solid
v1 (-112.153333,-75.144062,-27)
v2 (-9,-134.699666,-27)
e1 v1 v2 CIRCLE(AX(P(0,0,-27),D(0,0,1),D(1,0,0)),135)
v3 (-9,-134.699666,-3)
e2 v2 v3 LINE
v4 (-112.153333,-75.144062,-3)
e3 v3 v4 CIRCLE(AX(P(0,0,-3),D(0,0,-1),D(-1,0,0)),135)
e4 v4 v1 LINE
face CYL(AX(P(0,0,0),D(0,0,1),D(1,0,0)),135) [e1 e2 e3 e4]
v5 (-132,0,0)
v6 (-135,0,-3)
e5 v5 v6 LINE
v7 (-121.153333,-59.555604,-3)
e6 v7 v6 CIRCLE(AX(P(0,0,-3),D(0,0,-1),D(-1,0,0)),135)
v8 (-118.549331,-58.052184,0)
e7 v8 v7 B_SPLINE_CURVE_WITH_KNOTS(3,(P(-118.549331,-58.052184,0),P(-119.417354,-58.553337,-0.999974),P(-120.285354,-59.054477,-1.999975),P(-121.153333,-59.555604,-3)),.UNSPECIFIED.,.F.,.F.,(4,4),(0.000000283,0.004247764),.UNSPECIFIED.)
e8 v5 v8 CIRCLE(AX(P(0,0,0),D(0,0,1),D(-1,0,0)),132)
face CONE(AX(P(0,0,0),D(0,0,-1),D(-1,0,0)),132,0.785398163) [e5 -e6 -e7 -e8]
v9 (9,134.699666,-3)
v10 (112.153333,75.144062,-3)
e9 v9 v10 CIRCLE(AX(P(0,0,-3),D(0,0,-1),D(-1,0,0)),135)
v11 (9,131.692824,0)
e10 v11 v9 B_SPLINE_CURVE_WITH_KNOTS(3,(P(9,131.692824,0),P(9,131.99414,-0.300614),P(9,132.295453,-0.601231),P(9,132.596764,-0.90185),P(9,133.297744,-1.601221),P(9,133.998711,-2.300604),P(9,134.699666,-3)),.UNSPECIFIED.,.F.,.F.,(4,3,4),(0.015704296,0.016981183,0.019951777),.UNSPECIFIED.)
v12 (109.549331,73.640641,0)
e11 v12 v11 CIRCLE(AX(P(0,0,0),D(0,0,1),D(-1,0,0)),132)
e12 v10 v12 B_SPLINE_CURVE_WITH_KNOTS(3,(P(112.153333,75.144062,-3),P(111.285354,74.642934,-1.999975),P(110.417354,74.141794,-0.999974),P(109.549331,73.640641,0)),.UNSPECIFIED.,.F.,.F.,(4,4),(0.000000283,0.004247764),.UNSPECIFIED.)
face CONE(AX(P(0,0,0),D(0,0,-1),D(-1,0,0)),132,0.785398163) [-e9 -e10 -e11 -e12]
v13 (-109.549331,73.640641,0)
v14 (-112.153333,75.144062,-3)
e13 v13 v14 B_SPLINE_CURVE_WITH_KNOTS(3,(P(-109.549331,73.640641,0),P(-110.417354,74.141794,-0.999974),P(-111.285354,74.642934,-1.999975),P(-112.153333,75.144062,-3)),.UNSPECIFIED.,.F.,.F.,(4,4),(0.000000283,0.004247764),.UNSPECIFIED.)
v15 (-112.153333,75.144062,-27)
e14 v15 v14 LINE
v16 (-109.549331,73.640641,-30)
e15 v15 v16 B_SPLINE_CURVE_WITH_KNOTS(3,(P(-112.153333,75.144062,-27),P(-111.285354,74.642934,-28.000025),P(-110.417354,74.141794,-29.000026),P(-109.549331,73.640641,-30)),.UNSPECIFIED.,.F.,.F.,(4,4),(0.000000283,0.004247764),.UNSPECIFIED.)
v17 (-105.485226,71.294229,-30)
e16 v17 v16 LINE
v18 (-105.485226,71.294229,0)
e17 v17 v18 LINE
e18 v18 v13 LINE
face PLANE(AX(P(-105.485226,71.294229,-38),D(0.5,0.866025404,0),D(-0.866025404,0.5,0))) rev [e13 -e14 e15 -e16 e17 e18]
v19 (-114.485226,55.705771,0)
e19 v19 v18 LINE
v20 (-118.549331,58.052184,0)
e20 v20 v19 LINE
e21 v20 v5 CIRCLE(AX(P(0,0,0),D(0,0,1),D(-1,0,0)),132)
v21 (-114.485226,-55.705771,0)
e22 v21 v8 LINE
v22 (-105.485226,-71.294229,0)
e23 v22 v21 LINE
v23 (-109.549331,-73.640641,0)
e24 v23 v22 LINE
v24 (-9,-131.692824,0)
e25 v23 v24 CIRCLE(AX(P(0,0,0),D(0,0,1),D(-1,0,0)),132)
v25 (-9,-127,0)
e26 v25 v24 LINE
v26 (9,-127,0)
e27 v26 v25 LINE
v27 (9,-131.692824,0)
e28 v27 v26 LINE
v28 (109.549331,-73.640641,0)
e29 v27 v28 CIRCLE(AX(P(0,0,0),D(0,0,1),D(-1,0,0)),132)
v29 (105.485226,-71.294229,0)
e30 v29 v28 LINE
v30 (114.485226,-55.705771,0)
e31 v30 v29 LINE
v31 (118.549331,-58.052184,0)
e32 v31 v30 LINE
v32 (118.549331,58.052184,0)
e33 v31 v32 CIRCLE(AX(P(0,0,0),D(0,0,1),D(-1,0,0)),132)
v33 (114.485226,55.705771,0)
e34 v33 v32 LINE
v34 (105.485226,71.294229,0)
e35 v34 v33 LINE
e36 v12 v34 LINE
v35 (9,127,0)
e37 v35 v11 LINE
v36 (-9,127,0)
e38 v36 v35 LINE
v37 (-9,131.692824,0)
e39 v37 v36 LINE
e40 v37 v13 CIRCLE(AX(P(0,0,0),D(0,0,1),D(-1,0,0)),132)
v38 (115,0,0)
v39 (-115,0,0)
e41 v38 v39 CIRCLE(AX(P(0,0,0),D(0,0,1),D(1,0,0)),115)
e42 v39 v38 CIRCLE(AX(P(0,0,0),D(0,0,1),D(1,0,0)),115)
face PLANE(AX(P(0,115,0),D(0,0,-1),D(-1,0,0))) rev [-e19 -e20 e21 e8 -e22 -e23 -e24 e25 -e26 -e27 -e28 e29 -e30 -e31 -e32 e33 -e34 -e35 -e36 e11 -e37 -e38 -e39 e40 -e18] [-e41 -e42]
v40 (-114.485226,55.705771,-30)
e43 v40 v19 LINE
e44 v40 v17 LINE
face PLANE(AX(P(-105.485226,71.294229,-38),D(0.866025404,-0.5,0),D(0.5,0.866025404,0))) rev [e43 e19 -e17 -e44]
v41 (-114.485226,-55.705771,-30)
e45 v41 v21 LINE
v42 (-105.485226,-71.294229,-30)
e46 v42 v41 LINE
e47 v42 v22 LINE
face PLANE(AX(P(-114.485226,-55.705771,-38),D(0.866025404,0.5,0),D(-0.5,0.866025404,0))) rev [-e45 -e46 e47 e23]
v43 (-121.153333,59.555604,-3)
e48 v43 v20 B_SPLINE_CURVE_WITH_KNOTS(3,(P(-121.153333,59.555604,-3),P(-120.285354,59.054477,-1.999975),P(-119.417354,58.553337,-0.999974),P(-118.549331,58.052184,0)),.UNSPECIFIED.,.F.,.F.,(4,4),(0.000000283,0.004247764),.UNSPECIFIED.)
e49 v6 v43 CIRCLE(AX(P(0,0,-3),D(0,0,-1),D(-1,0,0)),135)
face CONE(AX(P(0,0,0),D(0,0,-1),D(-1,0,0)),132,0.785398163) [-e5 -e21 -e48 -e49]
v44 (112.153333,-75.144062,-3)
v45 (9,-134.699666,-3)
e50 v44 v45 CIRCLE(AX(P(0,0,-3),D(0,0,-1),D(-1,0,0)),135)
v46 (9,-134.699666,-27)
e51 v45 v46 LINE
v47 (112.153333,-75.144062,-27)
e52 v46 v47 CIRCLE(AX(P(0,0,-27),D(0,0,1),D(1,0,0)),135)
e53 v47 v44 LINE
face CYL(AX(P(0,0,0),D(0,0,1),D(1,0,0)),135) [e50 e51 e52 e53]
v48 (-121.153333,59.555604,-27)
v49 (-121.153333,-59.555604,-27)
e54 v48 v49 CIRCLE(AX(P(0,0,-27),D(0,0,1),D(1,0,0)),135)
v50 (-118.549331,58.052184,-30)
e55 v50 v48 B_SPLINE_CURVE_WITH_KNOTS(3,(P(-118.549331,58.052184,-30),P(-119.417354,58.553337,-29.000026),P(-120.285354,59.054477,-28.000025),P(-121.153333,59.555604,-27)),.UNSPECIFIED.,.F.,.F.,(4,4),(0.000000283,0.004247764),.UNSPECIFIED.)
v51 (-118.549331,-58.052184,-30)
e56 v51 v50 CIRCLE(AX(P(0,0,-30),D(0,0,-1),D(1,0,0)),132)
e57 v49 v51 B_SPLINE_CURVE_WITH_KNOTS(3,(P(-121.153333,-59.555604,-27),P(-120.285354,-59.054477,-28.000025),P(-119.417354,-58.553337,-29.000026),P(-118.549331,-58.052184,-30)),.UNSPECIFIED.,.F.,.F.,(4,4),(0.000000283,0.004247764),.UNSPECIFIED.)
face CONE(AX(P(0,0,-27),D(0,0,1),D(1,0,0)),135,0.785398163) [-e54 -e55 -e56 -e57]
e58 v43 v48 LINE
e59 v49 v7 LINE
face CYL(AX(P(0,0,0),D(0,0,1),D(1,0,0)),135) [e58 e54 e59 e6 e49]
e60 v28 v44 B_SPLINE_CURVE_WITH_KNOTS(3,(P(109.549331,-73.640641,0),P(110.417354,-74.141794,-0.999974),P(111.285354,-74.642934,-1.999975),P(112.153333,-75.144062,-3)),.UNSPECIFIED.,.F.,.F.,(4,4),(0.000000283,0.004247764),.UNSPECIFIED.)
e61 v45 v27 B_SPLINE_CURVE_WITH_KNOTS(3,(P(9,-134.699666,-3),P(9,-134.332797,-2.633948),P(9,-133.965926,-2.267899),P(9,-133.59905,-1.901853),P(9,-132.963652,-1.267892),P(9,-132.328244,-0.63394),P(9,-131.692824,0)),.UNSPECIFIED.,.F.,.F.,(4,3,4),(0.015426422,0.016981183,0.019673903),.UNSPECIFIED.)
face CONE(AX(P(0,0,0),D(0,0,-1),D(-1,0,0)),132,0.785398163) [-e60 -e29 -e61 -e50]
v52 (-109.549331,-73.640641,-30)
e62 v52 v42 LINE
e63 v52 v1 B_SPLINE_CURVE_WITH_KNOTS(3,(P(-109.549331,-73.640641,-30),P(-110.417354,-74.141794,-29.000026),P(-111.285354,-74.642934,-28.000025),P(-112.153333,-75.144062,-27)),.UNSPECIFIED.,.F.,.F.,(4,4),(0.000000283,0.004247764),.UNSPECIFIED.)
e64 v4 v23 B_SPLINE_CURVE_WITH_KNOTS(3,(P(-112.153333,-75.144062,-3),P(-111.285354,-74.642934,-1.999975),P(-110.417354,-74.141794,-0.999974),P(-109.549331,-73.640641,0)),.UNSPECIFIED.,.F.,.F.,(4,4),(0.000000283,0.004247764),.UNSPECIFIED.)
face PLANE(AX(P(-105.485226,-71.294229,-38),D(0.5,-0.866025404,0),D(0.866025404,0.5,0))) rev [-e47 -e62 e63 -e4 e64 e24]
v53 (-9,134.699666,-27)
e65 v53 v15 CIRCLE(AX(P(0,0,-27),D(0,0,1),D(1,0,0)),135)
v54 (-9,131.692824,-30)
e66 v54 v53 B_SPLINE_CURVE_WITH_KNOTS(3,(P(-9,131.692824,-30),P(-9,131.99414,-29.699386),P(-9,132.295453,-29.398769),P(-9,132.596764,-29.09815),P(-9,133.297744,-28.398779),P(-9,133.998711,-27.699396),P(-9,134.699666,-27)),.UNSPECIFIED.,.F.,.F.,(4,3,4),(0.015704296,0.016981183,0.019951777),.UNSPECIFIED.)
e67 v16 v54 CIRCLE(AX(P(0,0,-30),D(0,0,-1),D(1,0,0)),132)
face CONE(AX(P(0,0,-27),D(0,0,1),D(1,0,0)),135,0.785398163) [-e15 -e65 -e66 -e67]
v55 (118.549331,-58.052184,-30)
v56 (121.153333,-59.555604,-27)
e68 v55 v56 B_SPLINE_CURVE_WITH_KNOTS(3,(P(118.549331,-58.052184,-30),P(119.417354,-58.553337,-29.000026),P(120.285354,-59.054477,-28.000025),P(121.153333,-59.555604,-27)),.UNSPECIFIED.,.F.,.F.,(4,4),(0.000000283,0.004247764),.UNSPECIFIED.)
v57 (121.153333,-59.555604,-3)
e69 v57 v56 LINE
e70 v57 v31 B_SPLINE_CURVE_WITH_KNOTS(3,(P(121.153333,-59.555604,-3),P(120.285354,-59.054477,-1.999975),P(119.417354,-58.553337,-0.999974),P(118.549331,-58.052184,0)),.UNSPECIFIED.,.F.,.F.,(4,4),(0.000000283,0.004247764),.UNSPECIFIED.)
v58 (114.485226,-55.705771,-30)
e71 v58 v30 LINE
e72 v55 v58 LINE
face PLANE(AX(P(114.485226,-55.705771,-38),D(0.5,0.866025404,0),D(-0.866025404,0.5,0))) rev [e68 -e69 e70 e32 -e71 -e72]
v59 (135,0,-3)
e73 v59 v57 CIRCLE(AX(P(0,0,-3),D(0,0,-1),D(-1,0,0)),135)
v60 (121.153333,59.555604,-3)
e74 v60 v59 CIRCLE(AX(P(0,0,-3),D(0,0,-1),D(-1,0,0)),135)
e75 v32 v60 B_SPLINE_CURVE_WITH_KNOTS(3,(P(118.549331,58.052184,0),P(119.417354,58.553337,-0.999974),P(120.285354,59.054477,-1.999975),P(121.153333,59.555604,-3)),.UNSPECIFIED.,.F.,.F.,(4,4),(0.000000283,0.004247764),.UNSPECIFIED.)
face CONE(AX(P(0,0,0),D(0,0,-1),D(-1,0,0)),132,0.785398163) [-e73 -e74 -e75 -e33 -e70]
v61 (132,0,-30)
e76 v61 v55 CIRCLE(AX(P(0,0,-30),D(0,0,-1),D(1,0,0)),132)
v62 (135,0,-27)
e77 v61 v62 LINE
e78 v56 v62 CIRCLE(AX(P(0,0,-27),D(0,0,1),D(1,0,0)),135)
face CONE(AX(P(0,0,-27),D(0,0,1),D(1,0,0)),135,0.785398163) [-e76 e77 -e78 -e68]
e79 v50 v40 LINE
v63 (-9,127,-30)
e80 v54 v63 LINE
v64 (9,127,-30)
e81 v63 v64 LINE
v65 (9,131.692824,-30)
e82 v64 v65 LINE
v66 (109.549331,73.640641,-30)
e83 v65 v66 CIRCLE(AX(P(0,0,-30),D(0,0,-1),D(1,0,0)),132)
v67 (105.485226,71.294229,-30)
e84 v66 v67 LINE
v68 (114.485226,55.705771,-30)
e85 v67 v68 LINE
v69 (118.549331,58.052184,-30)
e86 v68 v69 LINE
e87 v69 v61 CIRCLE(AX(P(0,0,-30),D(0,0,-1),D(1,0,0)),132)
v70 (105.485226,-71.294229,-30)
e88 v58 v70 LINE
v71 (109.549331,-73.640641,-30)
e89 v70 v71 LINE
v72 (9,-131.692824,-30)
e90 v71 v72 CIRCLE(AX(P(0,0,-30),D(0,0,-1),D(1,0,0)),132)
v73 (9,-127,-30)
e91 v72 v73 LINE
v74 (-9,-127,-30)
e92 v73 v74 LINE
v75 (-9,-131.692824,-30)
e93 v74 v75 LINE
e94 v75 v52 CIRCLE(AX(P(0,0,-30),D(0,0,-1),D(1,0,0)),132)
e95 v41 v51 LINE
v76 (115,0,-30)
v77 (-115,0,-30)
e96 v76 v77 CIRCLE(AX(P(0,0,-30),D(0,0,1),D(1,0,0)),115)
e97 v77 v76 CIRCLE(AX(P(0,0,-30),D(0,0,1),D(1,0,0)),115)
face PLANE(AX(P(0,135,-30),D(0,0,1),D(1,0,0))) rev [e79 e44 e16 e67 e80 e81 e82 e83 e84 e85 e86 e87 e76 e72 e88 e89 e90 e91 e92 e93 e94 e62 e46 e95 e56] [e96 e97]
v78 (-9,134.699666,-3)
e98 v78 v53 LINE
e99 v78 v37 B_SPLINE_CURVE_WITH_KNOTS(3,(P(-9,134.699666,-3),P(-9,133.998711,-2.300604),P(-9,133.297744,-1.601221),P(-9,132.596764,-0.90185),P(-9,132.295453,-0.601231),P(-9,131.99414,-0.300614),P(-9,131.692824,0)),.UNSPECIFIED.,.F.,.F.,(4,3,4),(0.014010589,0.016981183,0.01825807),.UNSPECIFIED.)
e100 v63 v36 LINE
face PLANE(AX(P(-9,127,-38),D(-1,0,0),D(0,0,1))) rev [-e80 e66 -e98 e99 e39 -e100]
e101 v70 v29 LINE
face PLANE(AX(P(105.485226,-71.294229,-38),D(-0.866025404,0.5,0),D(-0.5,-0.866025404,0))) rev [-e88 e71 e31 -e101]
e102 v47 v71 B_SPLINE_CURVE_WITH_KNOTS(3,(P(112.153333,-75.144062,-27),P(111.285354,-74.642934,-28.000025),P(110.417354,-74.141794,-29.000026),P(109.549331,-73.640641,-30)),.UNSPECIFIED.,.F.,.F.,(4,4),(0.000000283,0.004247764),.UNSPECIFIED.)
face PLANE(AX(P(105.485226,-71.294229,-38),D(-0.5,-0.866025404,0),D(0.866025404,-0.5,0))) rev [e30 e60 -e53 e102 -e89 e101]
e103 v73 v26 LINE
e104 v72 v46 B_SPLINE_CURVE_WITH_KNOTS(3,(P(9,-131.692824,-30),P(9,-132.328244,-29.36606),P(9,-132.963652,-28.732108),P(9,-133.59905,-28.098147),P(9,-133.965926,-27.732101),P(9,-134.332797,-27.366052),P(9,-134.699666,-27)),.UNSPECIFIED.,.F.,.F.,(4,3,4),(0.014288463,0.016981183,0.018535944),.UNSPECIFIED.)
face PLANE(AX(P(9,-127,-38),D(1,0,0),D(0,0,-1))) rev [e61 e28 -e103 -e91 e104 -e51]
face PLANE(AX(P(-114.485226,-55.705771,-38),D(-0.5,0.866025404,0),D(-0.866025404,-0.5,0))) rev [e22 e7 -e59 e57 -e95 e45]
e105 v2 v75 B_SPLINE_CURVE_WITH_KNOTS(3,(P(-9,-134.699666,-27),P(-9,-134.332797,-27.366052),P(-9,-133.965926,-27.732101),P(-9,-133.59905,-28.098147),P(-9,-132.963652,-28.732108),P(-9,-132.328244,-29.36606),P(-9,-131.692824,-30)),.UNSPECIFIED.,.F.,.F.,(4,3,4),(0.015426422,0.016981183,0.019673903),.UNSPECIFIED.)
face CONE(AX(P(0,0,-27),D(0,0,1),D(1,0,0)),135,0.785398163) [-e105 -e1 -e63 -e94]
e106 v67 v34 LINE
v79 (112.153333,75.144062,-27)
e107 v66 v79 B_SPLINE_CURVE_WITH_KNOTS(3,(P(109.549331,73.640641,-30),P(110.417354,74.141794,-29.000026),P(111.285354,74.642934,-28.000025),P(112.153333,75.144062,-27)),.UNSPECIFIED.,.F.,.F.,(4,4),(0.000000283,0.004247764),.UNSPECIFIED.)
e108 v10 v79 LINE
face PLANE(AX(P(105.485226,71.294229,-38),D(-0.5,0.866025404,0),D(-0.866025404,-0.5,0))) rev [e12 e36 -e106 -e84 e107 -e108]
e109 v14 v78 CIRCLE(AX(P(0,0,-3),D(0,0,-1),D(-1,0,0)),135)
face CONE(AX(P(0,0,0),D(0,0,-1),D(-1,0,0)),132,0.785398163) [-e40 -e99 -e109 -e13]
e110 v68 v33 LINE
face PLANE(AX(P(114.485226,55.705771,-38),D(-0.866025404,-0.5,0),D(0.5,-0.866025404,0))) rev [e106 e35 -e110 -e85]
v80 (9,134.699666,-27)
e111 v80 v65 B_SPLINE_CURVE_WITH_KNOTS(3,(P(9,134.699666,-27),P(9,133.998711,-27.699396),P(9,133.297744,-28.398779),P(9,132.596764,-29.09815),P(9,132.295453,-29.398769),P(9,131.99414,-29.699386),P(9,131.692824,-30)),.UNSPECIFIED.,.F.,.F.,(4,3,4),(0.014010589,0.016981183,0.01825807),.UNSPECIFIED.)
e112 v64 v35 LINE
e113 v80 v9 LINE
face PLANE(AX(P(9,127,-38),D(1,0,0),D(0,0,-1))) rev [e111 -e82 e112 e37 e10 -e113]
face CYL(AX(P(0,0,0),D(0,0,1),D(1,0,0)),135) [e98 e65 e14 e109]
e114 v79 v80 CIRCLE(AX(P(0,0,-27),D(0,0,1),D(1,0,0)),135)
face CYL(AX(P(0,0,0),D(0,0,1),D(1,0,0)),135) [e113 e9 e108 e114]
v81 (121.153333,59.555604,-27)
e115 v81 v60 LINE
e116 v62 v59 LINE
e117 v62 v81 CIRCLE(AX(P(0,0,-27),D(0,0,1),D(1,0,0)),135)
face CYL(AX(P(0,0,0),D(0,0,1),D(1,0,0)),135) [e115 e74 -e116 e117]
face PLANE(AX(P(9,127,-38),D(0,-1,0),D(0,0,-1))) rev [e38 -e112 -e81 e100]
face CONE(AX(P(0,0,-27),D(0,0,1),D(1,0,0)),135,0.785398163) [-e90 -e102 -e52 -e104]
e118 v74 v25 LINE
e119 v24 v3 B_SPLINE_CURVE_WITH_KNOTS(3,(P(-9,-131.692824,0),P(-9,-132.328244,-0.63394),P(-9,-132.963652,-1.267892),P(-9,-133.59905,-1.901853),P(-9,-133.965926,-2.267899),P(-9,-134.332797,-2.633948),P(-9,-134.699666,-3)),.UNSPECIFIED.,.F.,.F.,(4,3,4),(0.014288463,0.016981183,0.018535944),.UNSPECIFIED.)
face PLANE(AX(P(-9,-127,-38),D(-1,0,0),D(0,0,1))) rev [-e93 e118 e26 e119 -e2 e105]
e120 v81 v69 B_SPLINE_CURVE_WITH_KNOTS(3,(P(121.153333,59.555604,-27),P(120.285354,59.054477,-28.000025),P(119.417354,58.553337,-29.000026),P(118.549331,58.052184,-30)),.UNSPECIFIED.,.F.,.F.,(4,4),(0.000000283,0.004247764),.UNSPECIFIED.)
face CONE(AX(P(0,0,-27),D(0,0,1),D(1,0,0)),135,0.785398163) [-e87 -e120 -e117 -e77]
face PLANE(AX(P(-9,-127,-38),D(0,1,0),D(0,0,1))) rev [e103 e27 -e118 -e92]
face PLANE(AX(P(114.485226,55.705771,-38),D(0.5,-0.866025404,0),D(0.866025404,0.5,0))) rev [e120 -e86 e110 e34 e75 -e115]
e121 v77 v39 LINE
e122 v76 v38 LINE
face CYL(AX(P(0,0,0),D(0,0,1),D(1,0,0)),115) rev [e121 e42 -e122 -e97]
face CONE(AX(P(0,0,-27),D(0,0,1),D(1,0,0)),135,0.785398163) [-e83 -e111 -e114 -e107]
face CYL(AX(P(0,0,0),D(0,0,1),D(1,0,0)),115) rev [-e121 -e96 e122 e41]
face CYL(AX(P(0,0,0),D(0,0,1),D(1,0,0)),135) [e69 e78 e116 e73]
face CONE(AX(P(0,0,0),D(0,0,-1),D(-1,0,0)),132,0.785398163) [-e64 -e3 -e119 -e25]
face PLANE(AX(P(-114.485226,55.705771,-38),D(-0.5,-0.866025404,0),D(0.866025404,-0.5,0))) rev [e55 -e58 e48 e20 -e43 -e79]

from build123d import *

# Parameters (mm, degrees)
SKETCH1_W          = 30
SKETCH1_H          = 20
CHAMFER1_SIZE      = 3
SKETCH2_W          = 18
SKETCH2_H          = 16
CUT_EXTRUDE1_DEPTH = 38
CIRPATTERN1_COUNT  = 6


with BuildPart() as part:
    # Sketch1 → Revolve1 (revolve)
    with BuildSketch(Plane(origin=(0, 0, 0), x_dir=(0, 0, -1), z_dir=(1, 0, 0)), mode=Mode.PRIVATE) as revolve1_sk:
        with Locations((15, 125)):
            Rectangle(SKETCH1_W, SKETCH1_H)
    revolve(revolve1_sk.sketch.rotate(Axis((0, 0, 0), (0, 0, -1)), 90), axis=Axis((0, 0, 0), (0, 0, -1)))

    # Chamfer1
    chamfer1_edges = [part.edges().sort_by_distance(p)[0] for p in [
        (-135, 0, -30),
        (-135, 0, 0),
    ]]
    chamfer(chamfer1_edges, length=CHAMFER1_SIZE)

    # Sketch2 → Cut-Extrude1 (cut)
    with BuildSketch(Plane.XY):
        with Locations((0, 135)):
            Rectangle(SKETCH2_W, SKETCH2_H)
    cut_extrude1 = extrude(amount=-CUT_EXTRUDE1_DEPTH, mode=Mode.SUBTRACT)

    # CirPattern1: Cut-Extrude1 ×6 about axis
    cirpattern1_axis = Axis((0, 0, 0), (0, 0, 1))
    for i in range(1, CIRPATTERN1_COUNT):
        add(cut_extrude1.rotate(cirpattern1_axis, i * 360 / CIRPATTERN1_COUNT), mode=Mode.SUBTRACT)


solid = part.part
